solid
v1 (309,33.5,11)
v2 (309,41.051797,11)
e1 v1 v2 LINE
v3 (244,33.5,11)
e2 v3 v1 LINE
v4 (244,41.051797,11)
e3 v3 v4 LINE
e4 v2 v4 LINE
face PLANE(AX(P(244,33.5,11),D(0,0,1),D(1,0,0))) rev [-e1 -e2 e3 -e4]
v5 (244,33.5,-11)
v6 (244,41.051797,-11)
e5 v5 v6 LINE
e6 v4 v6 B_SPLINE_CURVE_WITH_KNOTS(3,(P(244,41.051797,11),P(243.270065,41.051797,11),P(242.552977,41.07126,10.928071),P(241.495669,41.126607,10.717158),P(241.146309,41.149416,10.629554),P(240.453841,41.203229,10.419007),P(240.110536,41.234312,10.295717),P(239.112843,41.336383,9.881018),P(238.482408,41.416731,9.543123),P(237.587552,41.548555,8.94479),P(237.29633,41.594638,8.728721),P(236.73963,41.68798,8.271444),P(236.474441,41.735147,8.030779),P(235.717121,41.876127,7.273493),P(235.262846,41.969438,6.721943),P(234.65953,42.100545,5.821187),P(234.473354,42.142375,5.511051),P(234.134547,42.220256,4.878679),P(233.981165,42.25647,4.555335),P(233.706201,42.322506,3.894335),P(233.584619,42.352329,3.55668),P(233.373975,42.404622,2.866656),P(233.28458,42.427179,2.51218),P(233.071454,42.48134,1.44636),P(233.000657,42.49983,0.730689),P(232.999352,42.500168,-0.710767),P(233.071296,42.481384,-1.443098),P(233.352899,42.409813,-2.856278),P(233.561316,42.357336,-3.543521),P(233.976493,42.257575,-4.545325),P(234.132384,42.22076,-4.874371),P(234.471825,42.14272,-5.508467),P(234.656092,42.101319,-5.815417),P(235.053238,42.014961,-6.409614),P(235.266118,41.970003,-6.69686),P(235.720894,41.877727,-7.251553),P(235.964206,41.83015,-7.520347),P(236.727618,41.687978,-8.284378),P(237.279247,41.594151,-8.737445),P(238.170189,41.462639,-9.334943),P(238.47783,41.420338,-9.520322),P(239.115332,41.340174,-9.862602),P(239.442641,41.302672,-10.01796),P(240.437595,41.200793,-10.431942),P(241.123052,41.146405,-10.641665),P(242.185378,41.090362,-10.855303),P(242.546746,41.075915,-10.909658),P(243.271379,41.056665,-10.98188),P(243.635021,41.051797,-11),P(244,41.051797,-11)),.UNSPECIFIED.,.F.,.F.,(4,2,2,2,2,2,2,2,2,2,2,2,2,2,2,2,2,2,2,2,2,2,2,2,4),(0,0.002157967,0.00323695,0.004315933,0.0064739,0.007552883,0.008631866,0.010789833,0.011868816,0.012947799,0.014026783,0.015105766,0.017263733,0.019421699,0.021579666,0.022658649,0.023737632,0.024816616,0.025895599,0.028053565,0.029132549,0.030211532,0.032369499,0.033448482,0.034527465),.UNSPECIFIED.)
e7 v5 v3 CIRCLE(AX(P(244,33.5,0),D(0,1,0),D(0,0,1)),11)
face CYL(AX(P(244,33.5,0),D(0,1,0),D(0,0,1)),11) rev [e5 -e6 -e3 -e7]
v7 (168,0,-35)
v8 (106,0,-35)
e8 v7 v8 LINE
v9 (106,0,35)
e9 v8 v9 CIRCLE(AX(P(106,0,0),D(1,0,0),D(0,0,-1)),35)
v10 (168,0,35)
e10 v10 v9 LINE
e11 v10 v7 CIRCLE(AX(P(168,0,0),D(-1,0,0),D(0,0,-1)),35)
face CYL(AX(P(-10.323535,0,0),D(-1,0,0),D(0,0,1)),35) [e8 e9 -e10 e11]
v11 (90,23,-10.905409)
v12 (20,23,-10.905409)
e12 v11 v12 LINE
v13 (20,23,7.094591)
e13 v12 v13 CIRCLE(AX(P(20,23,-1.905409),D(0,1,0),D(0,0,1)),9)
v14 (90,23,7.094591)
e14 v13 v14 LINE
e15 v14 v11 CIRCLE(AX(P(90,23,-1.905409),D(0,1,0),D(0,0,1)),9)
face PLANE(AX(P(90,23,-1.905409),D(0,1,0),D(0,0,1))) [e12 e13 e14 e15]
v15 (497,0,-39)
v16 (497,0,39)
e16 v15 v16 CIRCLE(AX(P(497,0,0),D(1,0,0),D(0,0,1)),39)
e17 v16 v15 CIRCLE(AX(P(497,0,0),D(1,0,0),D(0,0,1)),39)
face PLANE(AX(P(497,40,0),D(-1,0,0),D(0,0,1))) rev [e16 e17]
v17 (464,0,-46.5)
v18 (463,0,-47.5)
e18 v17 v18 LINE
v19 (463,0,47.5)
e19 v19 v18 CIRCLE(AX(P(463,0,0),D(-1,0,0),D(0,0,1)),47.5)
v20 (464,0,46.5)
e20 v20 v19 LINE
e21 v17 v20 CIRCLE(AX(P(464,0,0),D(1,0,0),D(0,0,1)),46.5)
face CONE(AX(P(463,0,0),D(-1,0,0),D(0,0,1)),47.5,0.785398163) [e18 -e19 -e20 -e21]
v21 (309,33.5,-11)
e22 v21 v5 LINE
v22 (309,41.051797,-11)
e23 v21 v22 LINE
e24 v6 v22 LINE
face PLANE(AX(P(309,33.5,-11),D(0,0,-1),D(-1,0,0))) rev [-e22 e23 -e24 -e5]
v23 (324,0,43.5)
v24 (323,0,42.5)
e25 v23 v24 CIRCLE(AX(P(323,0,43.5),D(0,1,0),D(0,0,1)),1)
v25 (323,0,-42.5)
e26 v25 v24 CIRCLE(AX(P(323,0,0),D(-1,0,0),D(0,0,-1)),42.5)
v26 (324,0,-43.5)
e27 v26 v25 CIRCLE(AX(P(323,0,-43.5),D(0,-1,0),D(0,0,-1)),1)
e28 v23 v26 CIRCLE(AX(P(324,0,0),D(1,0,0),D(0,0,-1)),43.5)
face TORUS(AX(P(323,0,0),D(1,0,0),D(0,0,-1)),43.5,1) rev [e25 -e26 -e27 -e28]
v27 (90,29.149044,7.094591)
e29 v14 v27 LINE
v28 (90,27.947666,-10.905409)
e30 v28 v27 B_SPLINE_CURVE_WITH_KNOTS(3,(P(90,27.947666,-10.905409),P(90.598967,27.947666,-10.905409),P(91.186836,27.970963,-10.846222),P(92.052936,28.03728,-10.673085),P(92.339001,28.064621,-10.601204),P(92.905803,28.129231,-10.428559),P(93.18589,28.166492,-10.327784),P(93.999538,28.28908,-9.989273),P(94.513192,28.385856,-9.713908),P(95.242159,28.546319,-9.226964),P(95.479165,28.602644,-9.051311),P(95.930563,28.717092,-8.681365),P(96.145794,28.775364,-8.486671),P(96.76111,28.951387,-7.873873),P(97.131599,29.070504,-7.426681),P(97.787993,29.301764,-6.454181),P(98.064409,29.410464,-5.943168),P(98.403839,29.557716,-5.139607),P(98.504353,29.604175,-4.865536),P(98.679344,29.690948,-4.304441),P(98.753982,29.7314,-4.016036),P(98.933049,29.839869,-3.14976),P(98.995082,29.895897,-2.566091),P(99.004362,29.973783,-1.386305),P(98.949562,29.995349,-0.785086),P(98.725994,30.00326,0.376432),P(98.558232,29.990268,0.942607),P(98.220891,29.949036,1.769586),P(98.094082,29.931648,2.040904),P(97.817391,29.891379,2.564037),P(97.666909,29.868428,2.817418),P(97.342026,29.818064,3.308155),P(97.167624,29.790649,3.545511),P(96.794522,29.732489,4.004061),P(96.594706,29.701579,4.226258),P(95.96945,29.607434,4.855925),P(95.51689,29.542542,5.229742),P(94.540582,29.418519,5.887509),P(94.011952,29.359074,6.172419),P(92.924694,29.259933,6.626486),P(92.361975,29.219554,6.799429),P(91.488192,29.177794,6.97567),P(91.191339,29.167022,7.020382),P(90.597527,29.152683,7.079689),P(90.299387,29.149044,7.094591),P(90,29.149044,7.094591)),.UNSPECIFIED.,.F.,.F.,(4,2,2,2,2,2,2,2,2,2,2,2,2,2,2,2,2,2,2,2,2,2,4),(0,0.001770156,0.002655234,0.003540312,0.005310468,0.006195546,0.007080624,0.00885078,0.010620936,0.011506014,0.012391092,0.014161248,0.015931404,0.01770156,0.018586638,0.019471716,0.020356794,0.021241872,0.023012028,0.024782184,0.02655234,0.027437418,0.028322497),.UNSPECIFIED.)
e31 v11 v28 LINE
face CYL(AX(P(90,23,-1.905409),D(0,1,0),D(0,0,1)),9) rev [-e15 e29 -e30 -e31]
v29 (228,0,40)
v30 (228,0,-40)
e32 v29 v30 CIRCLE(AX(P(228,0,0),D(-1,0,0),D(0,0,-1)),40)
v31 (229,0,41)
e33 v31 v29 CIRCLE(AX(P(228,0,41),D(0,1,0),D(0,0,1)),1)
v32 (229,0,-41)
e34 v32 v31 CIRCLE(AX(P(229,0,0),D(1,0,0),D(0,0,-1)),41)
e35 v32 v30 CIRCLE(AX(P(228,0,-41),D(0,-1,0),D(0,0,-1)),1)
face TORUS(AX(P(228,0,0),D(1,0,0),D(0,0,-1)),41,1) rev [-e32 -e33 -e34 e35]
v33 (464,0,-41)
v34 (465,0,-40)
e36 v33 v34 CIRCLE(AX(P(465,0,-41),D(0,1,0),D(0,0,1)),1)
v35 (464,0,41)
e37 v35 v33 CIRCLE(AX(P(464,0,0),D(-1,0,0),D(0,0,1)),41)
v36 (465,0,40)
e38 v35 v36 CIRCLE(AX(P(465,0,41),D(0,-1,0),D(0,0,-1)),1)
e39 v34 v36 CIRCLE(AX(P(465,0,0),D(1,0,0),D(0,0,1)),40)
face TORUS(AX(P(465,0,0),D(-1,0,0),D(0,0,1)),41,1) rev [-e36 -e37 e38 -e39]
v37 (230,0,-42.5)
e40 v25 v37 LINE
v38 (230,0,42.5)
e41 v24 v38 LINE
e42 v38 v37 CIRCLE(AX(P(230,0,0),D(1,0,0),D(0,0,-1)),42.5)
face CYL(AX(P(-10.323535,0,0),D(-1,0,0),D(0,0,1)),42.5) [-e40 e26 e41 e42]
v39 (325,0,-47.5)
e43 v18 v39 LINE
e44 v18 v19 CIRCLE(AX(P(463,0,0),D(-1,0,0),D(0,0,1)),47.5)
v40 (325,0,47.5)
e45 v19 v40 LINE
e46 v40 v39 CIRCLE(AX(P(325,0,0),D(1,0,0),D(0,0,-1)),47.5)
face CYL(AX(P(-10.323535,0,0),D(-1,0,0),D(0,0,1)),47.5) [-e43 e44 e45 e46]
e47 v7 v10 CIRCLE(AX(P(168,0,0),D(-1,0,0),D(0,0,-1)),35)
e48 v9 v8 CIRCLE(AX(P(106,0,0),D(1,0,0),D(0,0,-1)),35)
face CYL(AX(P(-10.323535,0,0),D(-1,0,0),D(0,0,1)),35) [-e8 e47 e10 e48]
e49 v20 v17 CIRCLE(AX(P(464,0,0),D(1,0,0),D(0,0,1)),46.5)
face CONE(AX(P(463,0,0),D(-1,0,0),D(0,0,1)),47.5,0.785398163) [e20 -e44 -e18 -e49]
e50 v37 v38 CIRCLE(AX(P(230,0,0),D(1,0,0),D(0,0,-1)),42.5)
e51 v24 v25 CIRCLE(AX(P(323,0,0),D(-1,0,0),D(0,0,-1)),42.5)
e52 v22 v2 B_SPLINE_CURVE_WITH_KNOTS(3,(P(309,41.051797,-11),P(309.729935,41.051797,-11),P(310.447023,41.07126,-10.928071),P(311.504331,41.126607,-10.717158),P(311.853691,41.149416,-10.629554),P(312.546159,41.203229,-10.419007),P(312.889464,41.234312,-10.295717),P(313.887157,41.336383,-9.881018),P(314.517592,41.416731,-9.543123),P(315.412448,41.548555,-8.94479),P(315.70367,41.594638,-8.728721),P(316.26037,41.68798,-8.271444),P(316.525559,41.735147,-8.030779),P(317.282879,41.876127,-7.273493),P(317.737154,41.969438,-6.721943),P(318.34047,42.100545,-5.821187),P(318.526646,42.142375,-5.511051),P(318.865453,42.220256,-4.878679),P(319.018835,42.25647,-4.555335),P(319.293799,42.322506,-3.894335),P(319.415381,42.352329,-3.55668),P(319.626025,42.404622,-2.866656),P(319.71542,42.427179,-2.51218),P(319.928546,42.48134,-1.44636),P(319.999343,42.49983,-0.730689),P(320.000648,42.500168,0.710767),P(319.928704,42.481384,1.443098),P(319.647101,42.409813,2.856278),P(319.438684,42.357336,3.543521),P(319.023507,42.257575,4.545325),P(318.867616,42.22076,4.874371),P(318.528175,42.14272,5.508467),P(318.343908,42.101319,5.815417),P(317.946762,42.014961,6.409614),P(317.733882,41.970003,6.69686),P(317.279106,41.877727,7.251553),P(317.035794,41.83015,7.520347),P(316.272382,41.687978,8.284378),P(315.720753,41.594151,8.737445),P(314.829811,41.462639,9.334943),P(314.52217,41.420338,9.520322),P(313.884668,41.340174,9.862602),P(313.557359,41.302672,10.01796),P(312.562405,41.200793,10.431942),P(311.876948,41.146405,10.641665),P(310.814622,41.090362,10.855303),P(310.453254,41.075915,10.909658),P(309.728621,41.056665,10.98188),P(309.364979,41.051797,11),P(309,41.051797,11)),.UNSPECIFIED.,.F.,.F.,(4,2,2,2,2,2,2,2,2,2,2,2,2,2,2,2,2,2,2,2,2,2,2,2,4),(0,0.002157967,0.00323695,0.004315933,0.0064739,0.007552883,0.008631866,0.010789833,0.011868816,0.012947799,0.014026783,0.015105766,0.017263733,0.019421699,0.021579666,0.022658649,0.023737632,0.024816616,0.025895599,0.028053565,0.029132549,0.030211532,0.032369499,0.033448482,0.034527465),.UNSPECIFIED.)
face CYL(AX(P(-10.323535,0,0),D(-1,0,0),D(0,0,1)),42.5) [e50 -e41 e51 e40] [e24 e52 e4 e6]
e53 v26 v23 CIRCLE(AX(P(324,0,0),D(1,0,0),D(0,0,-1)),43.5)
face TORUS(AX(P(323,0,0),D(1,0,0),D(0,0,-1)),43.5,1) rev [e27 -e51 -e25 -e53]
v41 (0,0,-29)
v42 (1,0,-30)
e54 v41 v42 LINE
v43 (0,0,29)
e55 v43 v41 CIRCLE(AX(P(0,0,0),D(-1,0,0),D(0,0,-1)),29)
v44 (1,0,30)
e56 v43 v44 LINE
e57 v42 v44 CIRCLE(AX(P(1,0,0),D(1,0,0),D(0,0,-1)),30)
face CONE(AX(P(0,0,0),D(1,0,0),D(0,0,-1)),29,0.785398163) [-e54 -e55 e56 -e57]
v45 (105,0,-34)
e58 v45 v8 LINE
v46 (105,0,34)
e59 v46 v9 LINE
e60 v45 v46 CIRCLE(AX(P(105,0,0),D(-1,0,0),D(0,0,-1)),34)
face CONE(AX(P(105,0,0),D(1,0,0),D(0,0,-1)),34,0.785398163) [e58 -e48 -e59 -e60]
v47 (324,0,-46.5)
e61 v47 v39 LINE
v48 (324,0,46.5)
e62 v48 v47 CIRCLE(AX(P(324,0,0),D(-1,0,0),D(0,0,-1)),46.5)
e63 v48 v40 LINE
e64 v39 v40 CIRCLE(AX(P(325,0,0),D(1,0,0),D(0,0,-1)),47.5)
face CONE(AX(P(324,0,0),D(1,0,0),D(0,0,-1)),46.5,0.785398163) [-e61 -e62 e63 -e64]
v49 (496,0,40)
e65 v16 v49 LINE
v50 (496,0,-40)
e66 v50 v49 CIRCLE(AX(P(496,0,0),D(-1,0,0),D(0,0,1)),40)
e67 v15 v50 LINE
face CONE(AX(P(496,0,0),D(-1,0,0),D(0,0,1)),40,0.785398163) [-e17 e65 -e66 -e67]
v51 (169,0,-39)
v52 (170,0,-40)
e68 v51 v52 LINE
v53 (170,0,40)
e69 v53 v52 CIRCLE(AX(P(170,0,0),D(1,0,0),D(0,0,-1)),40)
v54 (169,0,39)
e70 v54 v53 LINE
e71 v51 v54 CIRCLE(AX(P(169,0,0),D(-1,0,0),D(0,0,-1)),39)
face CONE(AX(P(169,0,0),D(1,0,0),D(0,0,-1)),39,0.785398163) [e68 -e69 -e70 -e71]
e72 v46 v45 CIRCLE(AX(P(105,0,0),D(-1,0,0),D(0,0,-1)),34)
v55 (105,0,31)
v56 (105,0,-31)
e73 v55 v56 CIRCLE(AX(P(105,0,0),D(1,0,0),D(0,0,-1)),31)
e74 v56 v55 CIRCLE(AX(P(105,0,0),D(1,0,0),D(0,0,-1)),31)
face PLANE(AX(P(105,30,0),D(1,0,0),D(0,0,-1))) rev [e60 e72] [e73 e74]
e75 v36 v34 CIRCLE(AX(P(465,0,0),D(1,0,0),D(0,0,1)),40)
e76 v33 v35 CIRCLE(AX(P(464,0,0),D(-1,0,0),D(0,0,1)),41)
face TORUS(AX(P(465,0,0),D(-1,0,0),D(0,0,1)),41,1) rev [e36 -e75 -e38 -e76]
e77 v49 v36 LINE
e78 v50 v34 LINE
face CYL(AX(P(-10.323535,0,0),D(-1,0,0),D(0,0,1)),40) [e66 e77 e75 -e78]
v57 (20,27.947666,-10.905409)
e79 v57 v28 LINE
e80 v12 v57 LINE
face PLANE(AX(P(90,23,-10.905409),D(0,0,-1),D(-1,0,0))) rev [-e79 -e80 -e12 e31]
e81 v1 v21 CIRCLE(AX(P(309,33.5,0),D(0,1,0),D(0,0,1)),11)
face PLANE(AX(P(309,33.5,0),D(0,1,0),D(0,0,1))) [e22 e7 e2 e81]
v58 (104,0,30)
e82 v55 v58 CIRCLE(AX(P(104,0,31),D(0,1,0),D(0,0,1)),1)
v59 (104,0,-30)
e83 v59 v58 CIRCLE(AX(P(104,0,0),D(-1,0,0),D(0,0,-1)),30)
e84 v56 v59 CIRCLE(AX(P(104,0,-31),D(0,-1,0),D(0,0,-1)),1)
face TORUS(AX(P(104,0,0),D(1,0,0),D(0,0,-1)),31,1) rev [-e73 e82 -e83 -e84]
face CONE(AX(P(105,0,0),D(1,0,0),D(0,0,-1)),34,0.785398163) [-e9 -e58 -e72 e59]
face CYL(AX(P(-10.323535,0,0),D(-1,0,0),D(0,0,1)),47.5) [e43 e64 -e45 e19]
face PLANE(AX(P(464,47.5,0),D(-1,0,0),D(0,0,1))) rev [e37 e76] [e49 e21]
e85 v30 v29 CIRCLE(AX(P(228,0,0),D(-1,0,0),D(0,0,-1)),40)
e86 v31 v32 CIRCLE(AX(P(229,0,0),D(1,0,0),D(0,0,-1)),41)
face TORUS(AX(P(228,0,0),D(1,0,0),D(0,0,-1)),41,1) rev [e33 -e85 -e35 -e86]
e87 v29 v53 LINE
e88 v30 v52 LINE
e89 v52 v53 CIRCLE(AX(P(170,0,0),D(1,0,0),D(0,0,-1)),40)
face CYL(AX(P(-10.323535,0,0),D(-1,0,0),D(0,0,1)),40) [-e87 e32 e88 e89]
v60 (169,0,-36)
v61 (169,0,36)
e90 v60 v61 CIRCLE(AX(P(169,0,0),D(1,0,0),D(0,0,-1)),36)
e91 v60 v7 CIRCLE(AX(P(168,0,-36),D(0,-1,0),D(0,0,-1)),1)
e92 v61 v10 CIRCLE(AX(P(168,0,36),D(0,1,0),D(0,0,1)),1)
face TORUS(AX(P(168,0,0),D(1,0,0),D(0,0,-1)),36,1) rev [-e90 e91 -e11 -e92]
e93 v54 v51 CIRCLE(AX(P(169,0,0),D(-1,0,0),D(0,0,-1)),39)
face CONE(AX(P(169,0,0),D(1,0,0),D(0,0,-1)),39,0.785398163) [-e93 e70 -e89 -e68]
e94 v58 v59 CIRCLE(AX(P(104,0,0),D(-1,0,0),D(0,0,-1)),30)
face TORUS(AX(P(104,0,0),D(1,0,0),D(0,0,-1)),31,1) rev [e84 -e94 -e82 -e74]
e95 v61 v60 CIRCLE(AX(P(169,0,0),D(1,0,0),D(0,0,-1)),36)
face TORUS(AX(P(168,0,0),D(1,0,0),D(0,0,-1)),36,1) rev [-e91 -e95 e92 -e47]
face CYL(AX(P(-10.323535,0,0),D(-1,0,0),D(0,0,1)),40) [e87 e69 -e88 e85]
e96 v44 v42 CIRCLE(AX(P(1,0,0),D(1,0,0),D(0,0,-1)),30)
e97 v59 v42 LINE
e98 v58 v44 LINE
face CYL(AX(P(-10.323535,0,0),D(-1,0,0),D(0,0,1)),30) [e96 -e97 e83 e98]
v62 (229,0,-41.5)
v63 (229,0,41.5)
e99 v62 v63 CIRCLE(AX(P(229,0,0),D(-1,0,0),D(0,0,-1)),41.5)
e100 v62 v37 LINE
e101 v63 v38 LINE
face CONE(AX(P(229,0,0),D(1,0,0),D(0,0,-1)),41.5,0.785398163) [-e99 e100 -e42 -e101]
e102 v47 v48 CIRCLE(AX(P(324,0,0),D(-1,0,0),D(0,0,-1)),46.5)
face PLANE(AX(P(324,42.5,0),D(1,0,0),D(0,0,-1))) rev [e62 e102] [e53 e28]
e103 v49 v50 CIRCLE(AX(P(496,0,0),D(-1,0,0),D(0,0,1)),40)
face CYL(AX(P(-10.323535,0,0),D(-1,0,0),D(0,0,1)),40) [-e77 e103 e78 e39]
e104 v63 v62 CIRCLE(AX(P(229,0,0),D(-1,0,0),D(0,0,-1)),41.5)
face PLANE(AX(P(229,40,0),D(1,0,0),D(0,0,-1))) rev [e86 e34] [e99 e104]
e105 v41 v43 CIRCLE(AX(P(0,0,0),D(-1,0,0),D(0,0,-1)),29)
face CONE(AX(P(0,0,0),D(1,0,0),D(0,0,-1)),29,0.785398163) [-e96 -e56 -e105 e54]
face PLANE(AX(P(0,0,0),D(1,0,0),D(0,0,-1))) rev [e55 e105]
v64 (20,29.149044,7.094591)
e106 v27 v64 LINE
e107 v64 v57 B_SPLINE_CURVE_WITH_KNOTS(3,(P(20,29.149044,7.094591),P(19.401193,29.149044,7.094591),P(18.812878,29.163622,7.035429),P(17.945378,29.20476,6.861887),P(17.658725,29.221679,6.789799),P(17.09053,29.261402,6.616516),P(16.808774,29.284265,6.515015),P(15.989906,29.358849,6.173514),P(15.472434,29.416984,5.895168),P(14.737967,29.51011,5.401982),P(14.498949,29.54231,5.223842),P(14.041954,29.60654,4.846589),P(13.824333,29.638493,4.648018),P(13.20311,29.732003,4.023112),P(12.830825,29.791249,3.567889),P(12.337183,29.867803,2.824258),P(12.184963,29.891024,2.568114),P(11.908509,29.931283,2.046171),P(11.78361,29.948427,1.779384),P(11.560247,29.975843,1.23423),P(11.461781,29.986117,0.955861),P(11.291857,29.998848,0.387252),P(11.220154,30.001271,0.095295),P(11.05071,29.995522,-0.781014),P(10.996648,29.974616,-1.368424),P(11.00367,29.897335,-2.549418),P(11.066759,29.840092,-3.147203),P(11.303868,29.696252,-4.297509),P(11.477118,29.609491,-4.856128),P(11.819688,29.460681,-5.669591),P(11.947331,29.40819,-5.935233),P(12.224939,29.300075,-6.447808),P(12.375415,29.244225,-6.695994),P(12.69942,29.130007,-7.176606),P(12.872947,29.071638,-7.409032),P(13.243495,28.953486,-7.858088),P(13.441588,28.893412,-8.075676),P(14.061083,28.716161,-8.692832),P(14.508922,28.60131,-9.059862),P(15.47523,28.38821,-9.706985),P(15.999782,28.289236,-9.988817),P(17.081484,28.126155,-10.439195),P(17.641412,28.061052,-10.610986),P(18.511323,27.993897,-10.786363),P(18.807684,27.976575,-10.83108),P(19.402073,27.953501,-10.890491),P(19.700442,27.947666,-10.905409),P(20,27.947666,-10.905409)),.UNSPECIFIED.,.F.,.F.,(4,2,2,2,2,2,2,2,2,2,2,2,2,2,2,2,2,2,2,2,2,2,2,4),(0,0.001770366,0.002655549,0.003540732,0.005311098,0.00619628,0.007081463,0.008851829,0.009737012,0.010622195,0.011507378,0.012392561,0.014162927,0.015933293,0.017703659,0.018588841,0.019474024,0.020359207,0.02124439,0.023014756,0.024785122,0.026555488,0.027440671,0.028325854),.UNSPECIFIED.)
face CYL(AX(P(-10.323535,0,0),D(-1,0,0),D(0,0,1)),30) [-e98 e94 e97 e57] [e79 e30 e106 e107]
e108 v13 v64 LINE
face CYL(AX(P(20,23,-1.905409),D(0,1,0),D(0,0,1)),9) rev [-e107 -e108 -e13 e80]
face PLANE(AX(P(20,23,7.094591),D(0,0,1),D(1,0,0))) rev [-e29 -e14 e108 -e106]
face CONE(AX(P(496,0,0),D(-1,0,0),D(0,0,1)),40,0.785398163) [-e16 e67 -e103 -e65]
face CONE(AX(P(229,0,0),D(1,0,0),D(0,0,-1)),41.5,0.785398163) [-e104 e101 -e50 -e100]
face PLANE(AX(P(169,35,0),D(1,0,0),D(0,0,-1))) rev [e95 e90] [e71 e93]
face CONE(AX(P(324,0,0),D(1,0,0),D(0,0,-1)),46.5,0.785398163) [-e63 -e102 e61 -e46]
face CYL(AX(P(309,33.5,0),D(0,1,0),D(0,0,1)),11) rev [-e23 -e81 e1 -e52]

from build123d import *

# Parameters (mm, degrees)
CUT_EXTRUDE2_DEPTH = 9
CUT_EXTRUDE3_DEPTH = 7
CHAMFER1_SIZE      = 1
FILLET1_R          = 1


with BuildPart() as part:
    # Sketch1 → Revolve2 (revolve)
    with BuildSketch(Plane.XY, mode=Mode.PRIVATE) as revolve2_sk:
        Polygon((0, 0), (0, 30), (105, 30), (105, 35), (169, 35), (169, 40), (229, 40), (229, 42.5), (324, 42.5), (324, 47.5), (464, 47.5), (464, 40), (497, 40), (497, 0), align=None)
    revolve(revolve2_sk.sketch.rotate(Axis((-10.323535414, 0, 0), (1, 0, 0)), 90), axis=Axis((-10.323535414, 0, 0), (1, 0, 0)))

    # Sketch2 → Cut-Extrude2 (cut)
    with BuildSketch(Plane(origin=(0, 42.5, 0), x_dir=(1, 0, 0), z_dir=(0, 1, 0))):
        with BuildLine():
            Line((309, 11), (244, 11))
            ThreePointArc((244, 11), (233, 0), (244, -11))
            Line((244, -11), (309, -11))
            ThreePointArc((309, -11), (320, 0), (309, 11))
        make_face()
    extrude(amount=-CUT_EXTRUDE2_DEPTH, mode=Mode.SUBTRACT)

    # Sketch4 → Cut-Extrude3 (cut)
    with BuildSketch(Plane(origin=(0, 30, 0), x_dir=(1, 0, 0), z_dir=(0, 1, 0))):
        with BuildLine():
            Line((90, 10.905409347), (20, 10.905409347))
            ThreePointArc((20, 10.905409347), (11, 1.905409347), (20, -7.094590653))
            Line((20, -7.094590653), (90, -7.094590653))
            ThreePointArc((90, -7.094590653), (99, 1.905409347), (90, 10.905409347))
        make_face()
    extrude(amount=-CUT_EXTRUDE3_DEPTH, mode=Mode.SUBTRACT)

    # Chamfer1
    chamfer1_edges = [part.edges().sort_by_distance(p)[0] for p in [
        (497, 0, -40),
        (464, 0, -47.5),
        (324, 0, -47.5),
        (229, 0, -42.5),
        (169, 0, -40),
        (105, 0, -35),
        (0, 0, -30),
    ]]
    chamfer(chamfer1_edges, length=CHAMFER1_SIZE)

    # Fillet1
    fillet1_edges = [part.edges().sort_by_distance(p)[0] for p in [
        (464, 0, -40),
        (324, 0, -42.5),
        (229, 0, -40),
        (169, 0, -35),
        (105, 0, -30),
    ]]
    fillet(fillet1_edges, radius=FILLET1_R)


solid = part.part
